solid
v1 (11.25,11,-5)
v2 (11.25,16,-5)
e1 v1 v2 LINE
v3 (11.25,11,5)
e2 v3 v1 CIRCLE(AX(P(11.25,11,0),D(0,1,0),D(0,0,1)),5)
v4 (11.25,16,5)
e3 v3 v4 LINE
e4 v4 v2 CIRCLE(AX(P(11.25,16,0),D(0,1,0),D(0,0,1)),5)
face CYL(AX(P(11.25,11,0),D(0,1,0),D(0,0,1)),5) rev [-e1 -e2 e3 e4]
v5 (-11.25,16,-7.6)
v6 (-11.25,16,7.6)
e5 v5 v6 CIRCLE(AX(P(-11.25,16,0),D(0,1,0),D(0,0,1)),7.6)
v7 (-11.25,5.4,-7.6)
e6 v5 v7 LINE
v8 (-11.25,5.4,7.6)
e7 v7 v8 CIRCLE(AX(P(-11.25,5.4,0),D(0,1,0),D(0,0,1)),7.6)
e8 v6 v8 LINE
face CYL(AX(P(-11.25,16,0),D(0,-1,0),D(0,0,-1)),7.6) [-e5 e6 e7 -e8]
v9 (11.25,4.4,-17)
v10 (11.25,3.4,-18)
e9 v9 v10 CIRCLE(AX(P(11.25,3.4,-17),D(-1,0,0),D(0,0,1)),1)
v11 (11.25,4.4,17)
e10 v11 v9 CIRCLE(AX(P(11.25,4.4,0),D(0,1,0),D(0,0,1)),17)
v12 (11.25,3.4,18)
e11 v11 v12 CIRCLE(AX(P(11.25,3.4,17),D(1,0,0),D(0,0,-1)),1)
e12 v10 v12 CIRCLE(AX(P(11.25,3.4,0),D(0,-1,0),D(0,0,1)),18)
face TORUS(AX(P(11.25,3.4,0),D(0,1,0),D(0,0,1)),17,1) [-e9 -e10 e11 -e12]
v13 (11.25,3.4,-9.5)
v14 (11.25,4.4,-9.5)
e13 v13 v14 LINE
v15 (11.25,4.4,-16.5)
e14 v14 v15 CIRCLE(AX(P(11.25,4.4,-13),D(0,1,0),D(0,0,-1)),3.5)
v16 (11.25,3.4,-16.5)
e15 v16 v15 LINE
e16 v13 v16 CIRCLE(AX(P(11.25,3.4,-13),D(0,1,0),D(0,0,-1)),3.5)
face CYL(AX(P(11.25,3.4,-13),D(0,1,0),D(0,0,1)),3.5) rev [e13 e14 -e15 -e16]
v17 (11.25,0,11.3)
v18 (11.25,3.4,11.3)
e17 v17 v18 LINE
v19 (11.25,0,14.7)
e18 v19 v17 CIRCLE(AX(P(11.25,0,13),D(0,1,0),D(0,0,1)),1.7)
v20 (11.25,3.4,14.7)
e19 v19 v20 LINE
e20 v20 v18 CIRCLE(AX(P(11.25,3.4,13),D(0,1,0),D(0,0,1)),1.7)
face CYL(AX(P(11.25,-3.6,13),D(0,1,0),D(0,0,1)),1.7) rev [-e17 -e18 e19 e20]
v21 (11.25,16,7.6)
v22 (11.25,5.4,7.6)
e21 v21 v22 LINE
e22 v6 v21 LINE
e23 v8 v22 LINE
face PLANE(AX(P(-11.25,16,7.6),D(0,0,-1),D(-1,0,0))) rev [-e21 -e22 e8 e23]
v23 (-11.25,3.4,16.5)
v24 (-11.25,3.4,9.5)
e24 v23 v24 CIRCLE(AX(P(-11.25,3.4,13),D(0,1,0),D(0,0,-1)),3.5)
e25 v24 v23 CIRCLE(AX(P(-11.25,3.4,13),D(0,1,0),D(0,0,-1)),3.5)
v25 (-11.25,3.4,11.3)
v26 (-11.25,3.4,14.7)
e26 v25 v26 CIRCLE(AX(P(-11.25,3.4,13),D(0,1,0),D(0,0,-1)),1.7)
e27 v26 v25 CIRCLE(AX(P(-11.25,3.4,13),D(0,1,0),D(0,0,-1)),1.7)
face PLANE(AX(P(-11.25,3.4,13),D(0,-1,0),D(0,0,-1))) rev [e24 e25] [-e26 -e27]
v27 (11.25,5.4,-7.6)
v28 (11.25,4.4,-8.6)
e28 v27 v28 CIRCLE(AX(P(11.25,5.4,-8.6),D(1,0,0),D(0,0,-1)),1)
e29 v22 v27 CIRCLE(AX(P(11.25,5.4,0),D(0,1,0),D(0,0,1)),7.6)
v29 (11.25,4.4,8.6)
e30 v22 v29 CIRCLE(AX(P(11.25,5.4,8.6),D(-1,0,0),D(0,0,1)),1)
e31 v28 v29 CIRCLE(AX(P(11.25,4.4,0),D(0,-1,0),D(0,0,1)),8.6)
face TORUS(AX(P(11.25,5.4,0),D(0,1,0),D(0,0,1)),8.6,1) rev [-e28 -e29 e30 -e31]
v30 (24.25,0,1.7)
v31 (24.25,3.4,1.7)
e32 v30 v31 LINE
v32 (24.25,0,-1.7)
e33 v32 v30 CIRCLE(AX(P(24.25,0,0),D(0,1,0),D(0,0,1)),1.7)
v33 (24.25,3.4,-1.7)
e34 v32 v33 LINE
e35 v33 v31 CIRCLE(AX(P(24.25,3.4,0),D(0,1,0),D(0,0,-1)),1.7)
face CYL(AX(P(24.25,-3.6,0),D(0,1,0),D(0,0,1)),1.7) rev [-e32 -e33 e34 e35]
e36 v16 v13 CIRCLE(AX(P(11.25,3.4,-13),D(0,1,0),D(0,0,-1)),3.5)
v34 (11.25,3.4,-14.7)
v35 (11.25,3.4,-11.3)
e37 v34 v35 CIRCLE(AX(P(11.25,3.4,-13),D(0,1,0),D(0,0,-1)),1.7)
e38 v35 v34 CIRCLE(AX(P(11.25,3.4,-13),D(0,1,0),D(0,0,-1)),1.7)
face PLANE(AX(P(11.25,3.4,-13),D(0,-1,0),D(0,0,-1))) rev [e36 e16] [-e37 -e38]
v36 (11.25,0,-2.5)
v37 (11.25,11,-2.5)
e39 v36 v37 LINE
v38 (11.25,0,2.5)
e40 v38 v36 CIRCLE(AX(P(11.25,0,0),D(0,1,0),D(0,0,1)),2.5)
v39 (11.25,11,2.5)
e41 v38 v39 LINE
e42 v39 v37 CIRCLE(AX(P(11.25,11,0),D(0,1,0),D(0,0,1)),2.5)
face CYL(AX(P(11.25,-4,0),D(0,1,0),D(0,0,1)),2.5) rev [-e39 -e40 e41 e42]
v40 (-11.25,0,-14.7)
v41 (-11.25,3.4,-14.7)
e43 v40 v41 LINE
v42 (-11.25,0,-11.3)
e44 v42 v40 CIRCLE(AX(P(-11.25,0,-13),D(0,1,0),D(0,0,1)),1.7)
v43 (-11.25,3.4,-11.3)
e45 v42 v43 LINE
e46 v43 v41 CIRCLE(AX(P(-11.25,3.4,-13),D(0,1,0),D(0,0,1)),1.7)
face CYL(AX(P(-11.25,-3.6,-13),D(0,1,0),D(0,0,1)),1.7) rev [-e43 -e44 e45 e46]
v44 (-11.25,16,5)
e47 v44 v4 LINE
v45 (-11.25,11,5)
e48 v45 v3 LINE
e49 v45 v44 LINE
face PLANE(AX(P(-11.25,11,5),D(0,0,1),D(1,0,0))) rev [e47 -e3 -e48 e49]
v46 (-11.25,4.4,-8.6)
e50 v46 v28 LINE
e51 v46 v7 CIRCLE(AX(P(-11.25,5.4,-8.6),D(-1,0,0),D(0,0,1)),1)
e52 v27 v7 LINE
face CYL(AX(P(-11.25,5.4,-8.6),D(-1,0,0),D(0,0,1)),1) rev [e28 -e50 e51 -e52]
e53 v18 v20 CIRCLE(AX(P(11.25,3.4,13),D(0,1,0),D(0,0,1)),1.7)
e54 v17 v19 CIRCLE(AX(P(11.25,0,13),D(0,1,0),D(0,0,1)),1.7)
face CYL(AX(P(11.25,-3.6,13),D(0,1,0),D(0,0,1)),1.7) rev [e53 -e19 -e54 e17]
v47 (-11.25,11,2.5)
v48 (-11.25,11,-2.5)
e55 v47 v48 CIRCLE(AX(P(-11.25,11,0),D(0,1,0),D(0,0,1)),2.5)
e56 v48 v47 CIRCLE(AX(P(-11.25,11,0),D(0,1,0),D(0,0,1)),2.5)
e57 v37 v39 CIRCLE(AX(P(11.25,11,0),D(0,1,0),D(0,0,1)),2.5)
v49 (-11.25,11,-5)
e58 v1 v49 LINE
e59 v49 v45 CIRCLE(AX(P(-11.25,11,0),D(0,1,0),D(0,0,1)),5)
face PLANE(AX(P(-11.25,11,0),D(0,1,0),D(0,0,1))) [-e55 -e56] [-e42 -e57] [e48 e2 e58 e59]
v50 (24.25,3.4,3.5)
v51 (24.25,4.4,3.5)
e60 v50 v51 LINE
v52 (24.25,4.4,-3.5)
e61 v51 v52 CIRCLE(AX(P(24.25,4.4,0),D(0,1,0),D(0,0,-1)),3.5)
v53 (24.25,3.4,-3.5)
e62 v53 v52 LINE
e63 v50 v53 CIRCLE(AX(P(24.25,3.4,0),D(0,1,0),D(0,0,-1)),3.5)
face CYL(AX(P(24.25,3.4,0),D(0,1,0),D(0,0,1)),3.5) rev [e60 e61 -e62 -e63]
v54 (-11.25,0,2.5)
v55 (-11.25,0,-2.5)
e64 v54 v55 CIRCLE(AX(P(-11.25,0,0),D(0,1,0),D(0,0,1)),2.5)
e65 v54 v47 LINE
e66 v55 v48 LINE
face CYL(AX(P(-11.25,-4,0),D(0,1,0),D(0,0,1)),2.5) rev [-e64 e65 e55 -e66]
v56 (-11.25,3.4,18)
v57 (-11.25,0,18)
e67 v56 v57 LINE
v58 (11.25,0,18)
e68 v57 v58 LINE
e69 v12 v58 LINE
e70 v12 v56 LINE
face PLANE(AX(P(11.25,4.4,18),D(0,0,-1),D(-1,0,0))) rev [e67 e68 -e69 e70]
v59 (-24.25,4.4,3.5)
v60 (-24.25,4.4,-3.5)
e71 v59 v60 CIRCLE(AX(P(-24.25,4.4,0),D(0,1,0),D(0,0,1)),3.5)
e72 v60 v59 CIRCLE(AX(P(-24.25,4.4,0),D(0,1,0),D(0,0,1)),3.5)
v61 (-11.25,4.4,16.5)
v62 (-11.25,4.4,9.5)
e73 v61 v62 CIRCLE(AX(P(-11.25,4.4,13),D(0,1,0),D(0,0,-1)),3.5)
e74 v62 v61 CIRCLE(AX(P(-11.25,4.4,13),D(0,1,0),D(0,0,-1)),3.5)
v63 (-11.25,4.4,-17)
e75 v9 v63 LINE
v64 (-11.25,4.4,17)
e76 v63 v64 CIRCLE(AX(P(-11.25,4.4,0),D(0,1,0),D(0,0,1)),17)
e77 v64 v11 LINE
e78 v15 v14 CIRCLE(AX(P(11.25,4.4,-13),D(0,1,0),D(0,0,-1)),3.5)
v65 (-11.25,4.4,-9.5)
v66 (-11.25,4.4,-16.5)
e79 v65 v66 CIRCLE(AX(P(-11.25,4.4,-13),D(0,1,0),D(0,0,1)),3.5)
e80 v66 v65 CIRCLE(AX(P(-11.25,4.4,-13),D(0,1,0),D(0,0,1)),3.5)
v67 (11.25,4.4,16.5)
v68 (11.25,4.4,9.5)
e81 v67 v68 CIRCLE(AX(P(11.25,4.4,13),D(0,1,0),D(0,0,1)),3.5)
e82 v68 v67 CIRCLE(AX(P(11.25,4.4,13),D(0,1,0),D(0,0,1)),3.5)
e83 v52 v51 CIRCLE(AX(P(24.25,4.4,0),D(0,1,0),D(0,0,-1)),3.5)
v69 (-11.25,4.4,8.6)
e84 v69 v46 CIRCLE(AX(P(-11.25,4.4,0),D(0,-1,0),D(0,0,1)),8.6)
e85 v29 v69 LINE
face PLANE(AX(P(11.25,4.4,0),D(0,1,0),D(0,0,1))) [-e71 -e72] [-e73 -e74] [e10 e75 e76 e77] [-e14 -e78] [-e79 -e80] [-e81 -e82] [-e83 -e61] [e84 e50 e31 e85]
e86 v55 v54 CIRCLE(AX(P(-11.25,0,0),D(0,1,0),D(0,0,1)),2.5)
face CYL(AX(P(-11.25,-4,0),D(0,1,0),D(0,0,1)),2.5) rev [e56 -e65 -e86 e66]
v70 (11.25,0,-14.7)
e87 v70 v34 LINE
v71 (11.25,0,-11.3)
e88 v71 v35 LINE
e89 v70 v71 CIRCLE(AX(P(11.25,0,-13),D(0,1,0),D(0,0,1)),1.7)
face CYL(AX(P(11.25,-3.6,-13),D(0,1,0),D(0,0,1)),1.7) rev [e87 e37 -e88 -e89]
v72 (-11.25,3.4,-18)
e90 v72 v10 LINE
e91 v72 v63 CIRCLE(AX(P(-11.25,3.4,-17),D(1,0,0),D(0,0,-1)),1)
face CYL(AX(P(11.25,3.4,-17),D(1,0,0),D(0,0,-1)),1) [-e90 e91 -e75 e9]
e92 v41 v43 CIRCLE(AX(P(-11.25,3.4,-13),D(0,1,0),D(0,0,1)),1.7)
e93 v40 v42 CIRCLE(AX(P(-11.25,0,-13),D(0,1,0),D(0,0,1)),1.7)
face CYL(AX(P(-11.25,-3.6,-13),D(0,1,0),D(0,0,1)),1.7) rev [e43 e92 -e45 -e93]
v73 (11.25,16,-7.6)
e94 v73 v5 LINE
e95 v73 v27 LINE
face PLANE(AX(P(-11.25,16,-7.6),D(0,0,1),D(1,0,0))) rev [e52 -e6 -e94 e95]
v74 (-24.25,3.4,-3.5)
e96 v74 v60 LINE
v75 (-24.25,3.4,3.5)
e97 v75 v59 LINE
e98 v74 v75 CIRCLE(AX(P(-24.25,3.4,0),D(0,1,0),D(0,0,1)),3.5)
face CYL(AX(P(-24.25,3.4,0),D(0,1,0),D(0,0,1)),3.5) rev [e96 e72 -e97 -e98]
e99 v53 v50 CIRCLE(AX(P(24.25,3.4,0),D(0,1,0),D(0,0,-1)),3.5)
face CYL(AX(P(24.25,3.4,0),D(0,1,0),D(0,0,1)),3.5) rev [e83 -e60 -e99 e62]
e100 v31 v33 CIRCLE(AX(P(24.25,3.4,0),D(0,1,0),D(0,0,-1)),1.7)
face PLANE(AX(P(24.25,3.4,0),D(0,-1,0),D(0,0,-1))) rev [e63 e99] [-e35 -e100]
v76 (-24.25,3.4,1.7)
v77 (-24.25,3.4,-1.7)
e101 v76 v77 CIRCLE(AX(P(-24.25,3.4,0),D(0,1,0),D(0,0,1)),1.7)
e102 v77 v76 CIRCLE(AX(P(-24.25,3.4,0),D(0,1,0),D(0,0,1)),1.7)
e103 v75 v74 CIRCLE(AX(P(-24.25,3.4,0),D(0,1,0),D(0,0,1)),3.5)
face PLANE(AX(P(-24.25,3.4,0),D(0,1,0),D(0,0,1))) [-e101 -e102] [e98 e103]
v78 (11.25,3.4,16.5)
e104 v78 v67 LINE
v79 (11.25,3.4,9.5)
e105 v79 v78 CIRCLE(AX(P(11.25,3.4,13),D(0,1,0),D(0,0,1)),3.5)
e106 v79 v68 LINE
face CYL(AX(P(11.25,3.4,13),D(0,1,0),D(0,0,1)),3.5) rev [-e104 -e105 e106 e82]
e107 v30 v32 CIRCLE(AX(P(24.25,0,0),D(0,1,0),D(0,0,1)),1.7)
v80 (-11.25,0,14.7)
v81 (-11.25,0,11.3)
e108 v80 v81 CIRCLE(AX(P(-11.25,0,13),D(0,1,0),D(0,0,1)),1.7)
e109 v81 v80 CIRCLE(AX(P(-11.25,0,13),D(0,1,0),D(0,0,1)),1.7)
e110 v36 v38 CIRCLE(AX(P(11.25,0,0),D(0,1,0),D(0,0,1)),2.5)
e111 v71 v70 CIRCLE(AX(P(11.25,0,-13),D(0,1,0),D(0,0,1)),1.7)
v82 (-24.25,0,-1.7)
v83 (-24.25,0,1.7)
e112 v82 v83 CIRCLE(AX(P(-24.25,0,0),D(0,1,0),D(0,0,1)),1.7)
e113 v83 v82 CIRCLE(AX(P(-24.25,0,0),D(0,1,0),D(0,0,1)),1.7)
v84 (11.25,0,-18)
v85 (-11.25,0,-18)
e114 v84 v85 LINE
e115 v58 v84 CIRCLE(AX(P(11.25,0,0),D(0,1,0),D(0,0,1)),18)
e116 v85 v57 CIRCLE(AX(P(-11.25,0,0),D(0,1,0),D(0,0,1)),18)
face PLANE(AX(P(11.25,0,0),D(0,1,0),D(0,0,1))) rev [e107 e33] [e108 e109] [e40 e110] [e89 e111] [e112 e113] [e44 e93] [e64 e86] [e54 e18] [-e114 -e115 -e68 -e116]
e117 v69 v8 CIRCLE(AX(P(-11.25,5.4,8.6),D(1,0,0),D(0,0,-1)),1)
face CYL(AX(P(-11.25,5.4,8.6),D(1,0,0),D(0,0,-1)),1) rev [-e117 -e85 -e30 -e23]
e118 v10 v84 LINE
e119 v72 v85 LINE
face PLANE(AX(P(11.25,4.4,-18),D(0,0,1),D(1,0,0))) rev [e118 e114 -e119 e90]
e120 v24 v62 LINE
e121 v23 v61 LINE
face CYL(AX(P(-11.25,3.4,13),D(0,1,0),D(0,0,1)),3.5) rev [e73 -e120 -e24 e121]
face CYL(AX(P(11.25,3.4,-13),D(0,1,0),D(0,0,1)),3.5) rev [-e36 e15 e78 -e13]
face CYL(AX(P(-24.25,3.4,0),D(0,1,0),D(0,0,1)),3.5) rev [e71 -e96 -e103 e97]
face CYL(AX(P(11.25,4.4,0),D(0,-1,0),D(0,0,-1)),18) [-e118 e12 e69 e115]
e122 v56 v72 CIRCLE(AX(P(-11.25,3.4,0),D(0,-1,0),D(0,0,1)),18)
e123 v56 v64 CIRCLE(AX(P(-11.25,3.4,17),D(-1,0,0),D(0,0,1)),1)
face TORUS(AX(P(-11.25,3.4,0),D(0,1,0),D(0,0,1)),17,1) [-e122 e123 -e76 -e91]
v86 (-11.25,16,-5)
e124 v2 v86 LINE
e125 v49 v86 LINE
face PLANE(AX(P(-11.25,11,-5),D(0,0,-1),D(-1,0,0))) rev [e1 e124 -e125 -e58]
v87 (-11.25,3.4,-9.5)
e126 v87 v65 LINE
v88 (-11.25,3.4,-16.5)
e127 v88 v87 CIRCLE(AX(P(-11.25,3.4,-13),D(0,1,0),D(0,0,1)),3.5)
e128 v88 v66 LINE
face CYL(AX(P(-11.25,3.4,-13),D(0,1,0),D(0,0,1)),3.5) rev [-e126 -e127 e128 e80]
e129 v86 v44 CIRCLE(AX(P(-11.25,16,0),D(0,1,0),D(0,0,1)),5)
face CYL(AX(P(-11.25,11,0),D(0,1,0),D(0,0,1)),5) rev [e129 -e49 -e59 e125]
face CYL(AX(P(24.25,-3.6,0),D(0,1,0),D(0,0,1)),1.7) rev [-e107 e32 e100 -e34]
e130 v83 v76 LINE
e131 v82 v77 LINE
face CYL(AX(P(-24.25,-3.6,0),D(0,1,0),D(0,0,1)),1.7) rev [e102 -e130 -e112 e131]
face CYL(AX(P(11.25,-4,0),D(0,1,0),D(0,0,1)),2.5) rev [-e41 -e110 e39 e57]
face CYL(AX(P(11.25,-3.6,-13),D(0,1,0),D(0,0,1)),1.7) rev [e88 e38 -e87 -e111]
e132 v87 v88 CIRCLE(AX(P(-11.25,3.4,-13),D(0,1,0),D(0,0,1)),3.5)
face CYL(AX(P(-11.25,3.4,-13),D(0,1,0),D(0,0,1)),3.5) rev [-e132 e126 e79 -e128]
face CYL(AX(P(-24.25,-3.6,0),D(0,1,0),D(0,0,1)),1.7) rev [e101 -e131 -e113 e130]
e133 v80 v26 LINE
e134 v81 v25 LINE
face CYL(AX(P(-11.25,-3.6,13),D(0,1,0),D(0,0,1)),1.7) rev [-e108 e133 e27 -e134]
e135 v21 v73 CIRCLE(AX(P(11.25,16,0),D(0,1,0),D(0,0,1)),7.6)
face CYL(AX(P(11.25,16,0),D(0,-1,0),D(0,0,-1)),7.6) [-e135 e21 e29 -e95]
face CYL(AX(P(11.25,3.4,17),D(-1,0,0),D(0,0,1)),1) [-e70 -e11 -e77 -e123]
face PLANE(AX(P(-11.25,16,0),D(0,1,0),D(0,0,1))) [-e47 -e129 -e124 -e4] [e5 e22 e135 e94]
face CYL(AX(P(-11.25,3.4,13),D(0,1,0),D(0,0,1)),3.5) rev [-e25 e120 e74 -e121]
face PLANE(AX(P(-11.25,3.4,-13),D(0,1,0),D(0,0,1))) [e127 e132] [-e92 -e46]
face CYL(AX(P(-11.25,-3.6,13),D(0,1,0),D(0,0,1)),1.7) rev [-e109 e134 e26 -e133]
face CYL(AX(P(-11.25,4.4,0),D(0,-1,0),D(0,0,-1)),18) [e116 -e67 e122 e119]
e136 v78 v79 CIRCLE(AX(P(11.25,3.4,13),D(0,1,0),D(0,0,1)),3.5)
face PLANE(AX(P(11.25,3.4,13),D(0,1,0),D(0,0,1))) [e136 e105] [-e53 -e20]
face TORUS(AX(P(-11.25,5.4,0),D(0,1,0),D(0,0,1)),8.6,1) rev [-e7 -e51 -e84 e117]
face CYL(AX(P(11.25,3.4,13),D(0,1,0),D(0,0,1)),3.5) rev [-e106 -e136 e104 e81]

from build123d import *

# Parameters (mm, degrees)
OVAL_BASE_FLANGE_DEPTH           = 4.4
RAISED_OVAL_BOSS_DEPTH           = 11.6
OVAL_POCKET_R5_DEPTH             = 5
COUNTERBORE_SKETCH_R             = 3.5
MOUNTING_HOLE_COUNTERBORES_DEPTH = 1
MOUNTING_HOLES_SKETCH_R          = 1.7
MOUNTING_HOLES_3_4_DEPTH         = 7
THROUGH_SLOT_SKETCH_R            = 2.5
POCKET_THROUGH_SLOT_DEPTH        = 15
BOSS_ROOT_FILLET_R1_R            = 1


with BuildPart() as part:
    # Base Flange Sketch → Oval Base Flange (new body)
    with BuildSketch(Plane(origin=(0, 0, 0), x_dir=(1, 0, 0), z_dir=(0, 1, 0))):
        with BuildLine():
            Line((11.25, -18), (-11.25, -18))
            ThreePointArc((-11.25, -18), (-29.25, 0), (-11.25, 18))
            Line((-11.25, 18), (11.25, 18))
            ThreePointArc((11.25, 18), (29.25, 0), (11.25, -18))
        make_face()
    extrude(amount=OVAL_BASE_FLANGE_DEPTH)

    # Oval Boss Sketch → Raised Oval Boss (add)
    with BuildSketch(Plane(origin=(0, 4.4, 0), x_dir=(1, 0, 0), z_dir=(0, 1, 0))):
        with BuildLine():
            Line((-11.25, 7.6), (11.25, 7.6))
            ThreePointArc((11.25, 7.6), (18.85, 0), (11.25, -7.6))
            Line((11.25, -7.6), (-11.25, -7.6))
            ThreePointArc((-11.25, -7.6), (-18.85, 0), (-11.25, 7.6))
        make_face()
    extrude(amount=RAISED_OVAL_BOSS_DEPTH)

    # Oval Pocket Sketch → Oval Pocket R5 (cut)
    with BuildSketch(Plane(origin=(0, 16, 0), x_dir=(1, 0, 0), z_dir=(0, 1, 0))):
        with BuildLine():
            Line((-11.25, 5), (11.25, 5))
            ThreePointArc((11.25, 5), (16.25, 0), (11.25, -5))
            Line((11.25, -5), (-11.25, -5))
            ThreePointArc((-11.25, -5), (-16.25, 0), (-11.25, 5))
        make_face()
    extrude(amount=-OVAL_POCKET_R5_DEPTH, mode=Mode.SUBTRACT)

    # Counterbore Sketch → Mounting Hole Counterbores (cut)
    with BuildSketch(Plane(origin=(0, 4.4, 0), x_dir=(1, 0, 0), z_dir=(0, 1, 0))):
        with Locations(Location((-11.25, 13, 0), (0, 0, 270))):
            Circle(COUNTERBORE_SKETCH_R)
        with Locations(Location((11.25, 13, 0), (0, 0, 90))):
            Circle(COUNTERBORE_SKETCH_R)
        with Locations(Location((11.25, -13, 0), (0, 0, 270))):
            Circle(COUNTERBORE_SKETCH_R)
        with Locations(Location((-11.25, -13, 0), (0, 0, 90))):
            Circle(COUNTERBORE_SKETCH_R)
        with Locations(Location((-24.25, 0, 0), (0, 0, 270))):
            Circle(COUNTERBORE_SKETCH_R)
        with Locations(Location((24.25, 0, 0), (0, 0, 90))):
            Circle(COUNTERBORE_SKETCH_R)
    extrude(amount=-MOUNTING_HOLE_COUNTERBORES_DEPTH, mode=Mode.SUBTRACT)

    # Mounting Holes Sketch → Mounting Holes Ø3.4 (cut)
    with BuildSketch(Plane(origin=(0, 3.4, 0), x_dir=(1, 0, 0), z_dir=(0, 1, 0))):
        with Locations(Location((-11.25, 13, 0), (0, 0, 270))):
            Circle(MOUNTING_HOLES_SKETCH_R)
        with Locations(Location((11.25, 13, 0), (0, 0, 270))):
            Circle(MOUNTING_HOLES_SKETCH_R)
        with Locations(Location((11.25, -13, 0), (0, 0, 270))):
            Circle(MOUNTING_HOLES_SKETCH_R)
        with Locations(Location((-11.25, -13, 0), (0, 0, 270))):
            Circle(MOUNTING_HOLES_SKETCH_R)
        with Locations(Location((-24.25, 0, 0), (0, 0, 270))):
            Circle(MOUNTING_HOLES_SKETCH_R)
        with Locations(Location((24.25, 0, 0), (0, 0, 270))):
            Circle(MOUNTING_HOLES_SKETCH_R)
    extrude(amount=-MOUNTING_HOLES_3_4_DEPTH, mode=Mode.SUBTRACT)

    # Through Slot Sketch → Pocket Through Slot (cut)
    with BuildSketch(Plane(origin=(0, 11, 0), x_dir=(1, 0, 0), z_dir=(0, 1, 0))):
        with Locations(Location((-11.25, 0, 0), (0, 0, 270))):
            Circle(THROUGH_SLOT_SKETCH_R)
        with Locations(Location((11.25, 0, 0), (0, 0, 270))):
            Circle(THROUGH_SLOT_SKETCH_R)
    extrude(amount=-POCKET_THROUGH_SLOT_DEPTH, mode=Mode.SUBTRACT)

    # Boss Root Fillet R1
    boss_root_fillet_r1_edges = [part.edges().sort_by_distance(p)[0] for p in [
        (-29.25, 4.4, 0),
        (-18.85, 4.4, 0),
        (0, 4.4, 18),
        (0, 4.4, 7.6),
        (18.85, 4.4, 0),
        (0, 4.4, -7.6),
        (29.25, 4.4, 0),
        (0, 4.4, -18),
    ]]
    fillet(boss_root_fillet_r1_edges, radius=BOSS_ROOT_FILLET_R1_R)


solid = part.part
